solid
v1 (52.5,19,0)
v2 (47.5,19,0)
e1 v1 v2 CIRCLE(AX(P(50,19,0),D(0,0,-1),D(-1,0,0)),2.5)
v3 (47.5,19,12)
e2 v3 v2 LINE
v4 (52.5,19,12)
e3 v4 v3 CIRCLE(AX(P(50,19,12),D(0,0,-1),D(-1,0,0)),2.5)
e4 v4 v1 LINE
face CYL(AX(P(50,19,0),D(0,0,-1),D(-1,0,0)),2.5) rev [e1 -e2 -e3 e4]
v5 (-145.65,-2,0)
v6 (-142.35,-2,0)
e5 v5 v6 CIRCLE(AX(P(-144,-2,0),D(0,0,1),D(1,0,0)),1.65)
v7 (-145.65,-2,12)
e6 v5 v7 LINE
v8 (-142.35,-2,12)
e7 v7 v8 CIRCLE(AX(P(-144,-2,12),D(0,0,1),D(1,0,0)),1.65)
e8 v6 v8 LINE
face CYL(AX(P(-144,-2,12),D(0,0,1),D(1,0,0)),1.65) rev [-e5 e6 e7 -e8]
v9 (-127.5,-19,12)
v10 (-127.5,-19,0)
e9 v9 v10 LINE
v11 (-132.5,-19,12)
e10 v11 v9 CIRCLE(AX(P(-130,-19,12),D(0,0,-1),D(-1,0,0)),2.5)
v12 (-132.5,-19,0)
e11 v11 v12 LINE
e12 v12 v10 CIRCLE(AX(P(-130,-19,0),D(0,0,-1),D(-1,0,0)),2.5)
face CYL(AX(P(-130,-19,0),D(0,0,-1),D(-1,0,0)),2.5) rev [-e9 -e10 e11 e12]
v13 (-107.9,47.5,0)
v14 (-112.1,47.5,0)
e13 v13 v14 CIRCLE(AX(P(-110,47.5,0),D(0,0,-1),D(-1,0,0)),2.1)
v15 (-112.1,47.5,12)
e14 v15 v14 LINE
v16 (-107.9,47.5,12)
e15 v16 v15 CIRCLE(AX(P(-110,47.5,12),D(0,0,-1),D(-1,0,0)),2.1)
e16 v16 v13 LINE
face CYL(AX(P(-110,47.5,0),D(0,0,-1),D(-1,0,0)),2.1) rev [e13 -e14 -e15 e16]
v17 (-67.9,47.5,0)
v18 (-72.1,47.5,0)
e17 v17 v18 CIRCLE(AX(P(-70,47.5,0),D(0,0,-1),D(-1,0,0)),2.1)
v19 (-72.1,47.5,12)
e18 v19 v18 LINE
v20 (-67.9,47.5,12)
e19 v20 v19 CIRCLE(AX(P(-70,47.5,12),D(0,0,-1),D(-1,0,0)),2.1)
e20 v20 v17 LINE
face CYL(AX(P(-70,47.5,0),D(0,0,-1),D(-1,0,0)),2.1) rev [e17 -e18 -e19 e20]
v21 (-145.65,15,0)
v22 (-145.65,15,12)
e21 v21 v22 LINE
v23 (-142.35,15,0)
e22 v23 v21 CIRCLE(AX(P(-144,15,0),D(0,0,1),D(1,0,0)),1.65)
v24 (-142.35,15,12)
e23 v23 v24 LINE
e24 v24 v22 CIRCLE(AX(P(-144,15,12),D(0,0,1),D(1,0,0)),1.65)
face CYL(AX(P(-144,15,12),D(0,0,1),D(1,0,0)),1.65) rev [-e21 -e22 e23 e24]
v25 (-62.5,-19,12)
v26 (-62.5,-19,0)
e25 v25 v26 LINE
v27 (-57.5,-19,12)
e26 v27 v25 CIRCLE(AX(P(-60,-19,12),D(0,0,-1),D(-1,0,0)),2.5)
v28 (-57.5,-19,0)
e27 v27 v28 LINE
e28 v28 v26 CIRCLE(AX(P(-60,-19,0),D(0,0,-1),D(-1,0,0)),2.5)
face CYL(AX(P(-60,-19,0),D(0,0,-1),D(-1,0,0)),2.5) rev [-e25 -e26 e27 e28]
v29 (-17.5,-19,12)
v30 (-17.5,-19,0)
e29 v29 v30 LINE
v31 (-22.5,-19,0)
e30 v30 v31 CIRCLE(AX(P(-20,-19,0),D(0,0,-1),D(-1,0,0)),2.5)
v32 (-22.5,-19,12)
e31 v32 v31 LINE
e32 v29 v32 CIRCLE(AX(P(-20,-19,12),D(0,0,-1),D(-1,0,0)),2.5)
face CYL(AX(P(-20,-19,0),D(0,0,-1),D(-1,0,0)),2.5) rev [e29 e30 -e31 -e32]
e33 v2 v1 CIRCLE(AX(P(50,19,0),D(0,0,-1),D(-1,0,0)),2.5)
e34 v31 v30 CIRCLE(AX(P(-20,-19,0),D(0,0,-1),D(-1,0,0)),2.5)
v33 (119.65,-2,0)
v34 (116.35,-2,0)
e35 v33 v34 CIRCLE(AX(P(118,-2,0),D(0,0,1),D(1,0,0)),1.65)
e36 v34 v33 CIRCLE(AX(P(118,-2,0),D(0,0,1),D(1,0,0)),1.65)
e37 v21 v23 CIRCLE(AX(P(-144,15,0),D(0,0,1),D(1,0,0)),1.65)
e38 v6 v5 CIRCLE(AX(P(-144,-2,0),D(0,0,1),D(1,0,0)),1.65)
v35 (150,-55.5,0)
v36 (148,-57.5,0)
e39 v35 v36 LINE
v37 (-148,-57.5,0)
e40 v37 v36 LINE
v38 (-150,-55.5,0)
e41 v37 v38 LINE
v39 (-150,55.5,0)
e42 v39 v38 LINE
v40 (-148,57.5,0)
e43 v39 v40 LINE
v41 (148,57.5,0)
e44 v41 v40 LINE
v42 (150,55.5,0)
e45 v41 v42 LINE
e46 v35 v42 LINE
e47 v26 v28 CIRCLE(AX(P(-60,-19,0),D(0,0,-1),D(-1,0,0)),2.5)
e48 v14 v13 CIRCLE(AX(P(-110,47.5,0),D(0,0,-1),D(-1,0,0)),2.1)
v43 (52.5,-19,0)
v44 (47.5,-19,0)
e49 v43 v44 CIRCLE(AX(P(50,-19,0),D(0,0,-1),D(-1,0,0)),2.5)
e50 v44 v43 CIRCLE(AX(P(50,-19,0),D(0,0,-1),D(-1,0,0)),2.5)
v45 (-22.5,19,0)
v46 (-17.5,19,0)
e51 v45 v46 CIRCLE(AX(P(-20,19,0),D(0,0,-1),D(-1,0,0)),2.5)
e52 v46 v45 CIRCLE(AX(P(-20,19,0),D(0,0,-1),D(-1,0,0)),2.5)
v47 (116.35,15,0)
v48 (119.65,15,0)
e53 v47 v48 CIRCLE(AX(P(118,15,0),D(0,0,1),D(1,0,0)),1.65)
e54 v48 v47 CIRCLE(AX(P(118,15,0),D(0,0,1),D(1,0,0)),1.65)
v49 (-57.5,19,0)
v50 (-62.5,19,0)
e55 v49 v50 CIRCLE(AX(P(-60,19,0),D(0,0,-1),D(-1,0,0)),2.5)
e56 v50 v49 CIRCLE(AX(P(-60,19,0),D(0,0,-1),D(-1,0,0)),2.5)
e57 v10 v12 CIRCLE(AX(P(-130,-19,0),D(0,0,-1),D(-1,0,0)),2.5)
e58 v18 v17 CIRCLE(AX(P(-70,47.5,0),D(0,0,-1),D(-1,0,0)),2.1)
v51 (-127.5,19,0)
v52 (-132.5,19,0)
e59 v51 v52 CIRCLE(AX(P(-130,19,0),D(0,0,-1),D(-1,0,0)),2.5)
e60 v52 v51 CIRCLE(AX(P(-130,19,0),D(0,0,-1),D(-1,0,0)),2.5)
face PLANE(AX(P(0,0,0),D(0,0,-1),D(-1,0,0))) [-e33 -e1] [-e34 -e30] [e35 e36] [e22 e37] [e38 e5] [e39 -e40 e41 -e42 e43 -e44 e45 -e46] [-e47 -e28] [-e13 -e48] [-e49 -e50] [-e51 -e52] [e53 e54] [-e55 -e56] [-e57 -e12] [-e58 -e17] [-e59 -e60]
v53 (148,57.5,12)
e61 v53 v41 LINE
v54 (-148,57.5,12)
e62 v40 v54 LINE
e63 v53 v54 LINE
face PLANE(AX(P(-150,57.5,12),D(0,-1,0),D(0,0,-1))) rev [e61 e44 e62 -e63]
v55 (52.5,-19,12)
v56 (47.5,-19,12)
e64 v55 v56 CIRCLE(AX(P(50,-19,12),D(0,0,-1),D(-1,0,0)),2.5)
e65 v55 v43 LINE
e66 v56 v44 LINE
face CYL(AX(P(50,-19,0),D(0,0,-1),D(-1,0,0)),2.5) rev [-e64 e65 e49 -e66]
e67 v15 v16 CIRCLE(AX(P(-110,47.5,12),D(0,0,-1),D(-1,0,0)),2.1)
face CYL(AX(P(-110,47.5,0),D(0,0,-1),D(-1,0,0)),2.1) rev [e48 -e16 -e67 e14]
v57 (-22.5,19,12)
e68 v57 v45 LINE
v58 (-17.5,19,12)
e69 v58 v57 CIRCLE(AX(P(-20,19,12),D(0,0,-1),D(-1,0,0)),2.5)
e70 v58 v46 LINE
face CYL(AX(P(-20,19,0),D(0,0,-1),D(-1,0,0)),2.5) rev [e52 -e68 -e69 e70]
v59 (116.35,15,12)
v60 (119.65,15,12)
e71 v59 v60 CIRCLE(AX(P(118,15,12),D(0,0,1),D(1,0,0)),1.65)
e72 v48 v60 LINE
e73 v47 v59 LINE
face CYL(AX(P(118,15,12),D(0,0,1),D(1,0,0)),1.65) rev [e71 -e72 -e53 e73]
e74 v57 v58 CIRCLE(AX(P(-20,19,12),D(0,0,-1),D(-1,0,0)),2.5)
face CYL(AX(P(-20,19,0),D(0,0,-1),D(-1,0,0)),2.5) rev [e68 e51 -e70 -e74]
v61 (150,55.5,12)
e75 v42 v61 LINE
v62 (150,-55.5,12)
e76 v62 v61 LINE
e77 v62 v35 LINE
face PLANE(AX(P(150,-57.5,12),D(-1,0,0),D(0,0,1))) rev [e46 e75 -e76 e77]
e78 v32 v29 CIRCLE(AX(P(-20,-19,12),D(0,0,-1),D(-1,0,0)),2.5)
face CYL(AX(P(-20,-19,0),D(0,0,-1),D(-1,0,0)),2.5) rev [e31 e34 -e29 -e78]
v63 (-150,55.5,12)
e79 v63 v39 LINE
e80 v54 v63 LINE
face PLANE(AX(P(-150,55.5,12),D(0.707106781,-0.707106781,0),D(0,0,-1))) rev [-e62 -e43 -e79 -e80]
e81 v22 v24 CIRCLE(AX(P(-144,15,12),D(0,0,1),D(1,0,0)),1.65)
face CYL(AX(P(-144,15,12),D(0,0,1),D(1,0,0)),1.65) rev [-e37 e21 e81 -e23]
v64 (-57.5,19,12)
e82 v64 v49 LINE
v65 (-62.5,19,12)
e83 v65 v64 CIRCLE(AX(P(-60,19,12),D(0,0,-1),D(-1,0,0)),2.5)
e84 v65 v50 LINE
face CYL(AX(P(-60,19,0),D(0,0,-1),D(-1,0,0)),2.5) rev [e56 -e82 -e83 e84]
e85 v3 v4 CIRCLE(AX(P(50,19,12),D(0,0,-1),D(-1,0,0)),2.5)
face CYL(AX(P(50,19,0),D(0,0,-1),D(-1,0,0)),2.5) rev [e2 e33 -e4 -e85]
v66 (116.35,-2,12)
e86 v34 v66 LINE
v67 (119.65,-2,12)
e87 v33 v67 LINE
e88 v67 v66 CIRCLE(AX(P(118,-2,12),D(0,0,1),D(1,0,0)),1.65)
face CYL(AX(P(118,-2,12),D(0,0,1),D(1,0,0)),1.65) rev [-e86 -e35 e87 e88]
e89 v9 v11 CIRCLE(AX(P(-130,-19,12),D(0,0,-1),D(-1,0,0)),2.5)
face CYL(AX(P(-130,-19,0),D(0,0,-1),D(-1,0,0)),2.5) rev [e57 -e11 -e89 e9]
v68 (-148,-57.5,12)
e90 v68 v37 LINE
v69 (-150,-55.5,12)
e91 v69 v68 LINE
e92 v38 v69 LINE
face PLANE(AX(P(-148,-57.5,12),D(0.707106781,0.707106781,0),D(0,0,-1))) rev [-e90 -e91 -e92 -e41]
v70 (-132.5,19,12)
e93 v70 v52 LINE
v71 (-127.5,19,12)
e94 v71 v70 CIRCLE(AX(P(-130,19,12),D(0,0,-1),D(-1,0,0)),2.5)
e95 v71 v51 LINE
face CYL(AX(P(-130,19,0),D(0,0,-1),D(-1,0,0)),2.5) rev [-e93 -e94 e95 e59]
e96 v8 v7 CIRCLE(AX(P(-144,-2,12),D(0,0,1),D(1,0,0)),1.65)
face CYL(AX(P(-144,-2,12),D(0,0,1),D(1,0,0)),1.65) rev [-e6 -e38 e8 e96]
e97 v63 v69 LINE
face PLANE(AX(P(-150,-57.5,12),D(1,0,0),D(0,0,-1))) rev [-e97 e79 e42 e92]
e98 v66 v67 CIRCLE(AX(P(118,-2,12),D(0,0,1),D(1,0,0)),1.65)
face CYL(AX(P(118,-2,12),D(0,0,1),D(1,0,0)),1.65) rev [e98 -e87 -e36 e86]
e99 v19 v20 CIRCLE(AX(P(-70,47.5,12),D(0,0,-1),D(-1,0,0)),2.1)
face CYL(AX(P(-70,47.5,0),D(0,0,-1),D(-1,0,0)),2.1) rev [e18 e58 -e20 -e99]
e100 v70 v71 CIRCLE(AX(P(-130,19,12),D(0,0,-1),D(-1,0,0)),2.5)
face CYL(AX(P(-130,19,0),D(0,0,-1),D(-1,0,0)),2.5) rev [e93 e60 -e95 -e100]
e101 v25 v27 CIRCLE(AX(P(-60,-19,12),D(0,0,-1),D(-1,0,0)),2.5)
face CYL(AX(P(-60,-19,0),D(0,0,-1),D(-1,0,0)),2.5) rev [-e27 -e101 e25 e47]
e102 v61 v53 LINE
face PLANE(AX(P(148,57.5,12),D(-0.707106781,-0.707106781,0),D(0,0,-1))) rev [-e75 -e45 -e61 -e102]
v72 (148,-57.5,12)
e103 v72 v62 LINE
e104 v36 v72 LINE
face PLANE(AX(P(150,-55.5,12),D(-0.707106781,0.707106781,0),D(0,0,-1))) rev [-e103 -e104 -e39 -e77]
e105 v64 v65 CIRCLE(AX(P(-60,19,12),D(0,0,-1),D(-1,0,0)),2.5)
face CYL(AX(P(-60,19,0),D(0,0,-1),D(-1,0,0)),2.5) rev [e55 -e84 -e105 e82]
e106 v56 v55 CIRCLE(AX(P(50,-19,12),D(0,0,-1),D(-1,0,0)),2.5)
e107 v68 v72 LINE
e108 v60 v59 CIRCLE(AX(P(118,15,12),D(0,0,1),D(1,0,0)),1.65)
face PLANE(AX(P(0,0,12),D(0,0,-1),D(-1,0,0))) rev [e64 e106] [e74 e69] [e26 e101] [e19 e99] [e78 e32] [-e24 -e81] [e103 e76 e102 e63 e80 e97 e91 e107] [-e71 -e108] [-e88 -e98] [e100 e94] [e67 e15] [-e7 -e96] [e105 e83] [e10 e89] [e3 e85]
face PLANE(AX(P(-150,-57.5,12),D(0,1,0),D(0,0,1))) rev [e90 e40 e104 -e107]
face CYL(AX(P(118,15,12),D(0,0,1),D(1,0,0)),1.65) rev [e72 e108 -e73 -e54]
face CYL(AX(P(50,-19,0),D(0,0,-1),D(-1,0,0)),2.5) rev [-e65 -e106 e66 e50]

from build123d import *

# Parameters (mm, degrees)
SKETCH_1_W         = 300
SKETCH_1_H         = 115
EXTRUDE_1_DEPTH    = 12
HOLE_WIZARD_M6_1_D = 5
HOLE_WIZARD_M4_2_D = 3.3
HOLE_WIZARD_M5_1_D = 4.2
CHAMFER_1_SIZE     = 2


with BuildPart() as part:
    # 草图1 → 凸台-拉伸1 (new body)
    with BuildSketch(Plane.XY):
        Rectangle(SKETCH_1_W, SKETCH_1_H)
    extrude(amount=EXTRUDE_1_DEPTH)

    # M6 螺纹孔1 (through all)
    with Locations(Plane(origin=(0, 0, 0), x_dir=(-1, 0, 0), z_dir=(0, 0, -1))):
        with Locations((130, 19), (60, -19), (60, 19), (130, -19), (20, 19), (-50, -19), (-50, 19), (20, -19)):
            Hole(HOLE_WIZARD_M6_1_D / 2)

    # M4 螺纹孔2 (through all)
    with Locations(Plane.XY.offset(12)):
        with Locations((-144, 15), (-144, -2), (118, 15), (118, -2)):
            Hole(HOLE_WIZARD_M4_2_D / 2)

    # M5 螺纹孔1 (through all)
    with Locations(Plane(origin=(0, 0, 0), x_dir=(-1, 0, 0), z_dir=(0, 0, -1))):
        with Locations((110, 47.5), (70, 47.5)):
            Hole(HOLE_WIZARD_M5_1_D / 2)

    # 倒角1
    chamfer_1_edges = [part.edges().sort_by_distance(p)[0] for p in [
        (150, -57.5, 6),
        (-150, -57.5, 6),
        (-150, 57.5, 6),
        (150, 57.5, 6),
    ]]
    chamfer(chamfer_1_edges, length=CHAMFER_1_SIZE)


solid = part.part
